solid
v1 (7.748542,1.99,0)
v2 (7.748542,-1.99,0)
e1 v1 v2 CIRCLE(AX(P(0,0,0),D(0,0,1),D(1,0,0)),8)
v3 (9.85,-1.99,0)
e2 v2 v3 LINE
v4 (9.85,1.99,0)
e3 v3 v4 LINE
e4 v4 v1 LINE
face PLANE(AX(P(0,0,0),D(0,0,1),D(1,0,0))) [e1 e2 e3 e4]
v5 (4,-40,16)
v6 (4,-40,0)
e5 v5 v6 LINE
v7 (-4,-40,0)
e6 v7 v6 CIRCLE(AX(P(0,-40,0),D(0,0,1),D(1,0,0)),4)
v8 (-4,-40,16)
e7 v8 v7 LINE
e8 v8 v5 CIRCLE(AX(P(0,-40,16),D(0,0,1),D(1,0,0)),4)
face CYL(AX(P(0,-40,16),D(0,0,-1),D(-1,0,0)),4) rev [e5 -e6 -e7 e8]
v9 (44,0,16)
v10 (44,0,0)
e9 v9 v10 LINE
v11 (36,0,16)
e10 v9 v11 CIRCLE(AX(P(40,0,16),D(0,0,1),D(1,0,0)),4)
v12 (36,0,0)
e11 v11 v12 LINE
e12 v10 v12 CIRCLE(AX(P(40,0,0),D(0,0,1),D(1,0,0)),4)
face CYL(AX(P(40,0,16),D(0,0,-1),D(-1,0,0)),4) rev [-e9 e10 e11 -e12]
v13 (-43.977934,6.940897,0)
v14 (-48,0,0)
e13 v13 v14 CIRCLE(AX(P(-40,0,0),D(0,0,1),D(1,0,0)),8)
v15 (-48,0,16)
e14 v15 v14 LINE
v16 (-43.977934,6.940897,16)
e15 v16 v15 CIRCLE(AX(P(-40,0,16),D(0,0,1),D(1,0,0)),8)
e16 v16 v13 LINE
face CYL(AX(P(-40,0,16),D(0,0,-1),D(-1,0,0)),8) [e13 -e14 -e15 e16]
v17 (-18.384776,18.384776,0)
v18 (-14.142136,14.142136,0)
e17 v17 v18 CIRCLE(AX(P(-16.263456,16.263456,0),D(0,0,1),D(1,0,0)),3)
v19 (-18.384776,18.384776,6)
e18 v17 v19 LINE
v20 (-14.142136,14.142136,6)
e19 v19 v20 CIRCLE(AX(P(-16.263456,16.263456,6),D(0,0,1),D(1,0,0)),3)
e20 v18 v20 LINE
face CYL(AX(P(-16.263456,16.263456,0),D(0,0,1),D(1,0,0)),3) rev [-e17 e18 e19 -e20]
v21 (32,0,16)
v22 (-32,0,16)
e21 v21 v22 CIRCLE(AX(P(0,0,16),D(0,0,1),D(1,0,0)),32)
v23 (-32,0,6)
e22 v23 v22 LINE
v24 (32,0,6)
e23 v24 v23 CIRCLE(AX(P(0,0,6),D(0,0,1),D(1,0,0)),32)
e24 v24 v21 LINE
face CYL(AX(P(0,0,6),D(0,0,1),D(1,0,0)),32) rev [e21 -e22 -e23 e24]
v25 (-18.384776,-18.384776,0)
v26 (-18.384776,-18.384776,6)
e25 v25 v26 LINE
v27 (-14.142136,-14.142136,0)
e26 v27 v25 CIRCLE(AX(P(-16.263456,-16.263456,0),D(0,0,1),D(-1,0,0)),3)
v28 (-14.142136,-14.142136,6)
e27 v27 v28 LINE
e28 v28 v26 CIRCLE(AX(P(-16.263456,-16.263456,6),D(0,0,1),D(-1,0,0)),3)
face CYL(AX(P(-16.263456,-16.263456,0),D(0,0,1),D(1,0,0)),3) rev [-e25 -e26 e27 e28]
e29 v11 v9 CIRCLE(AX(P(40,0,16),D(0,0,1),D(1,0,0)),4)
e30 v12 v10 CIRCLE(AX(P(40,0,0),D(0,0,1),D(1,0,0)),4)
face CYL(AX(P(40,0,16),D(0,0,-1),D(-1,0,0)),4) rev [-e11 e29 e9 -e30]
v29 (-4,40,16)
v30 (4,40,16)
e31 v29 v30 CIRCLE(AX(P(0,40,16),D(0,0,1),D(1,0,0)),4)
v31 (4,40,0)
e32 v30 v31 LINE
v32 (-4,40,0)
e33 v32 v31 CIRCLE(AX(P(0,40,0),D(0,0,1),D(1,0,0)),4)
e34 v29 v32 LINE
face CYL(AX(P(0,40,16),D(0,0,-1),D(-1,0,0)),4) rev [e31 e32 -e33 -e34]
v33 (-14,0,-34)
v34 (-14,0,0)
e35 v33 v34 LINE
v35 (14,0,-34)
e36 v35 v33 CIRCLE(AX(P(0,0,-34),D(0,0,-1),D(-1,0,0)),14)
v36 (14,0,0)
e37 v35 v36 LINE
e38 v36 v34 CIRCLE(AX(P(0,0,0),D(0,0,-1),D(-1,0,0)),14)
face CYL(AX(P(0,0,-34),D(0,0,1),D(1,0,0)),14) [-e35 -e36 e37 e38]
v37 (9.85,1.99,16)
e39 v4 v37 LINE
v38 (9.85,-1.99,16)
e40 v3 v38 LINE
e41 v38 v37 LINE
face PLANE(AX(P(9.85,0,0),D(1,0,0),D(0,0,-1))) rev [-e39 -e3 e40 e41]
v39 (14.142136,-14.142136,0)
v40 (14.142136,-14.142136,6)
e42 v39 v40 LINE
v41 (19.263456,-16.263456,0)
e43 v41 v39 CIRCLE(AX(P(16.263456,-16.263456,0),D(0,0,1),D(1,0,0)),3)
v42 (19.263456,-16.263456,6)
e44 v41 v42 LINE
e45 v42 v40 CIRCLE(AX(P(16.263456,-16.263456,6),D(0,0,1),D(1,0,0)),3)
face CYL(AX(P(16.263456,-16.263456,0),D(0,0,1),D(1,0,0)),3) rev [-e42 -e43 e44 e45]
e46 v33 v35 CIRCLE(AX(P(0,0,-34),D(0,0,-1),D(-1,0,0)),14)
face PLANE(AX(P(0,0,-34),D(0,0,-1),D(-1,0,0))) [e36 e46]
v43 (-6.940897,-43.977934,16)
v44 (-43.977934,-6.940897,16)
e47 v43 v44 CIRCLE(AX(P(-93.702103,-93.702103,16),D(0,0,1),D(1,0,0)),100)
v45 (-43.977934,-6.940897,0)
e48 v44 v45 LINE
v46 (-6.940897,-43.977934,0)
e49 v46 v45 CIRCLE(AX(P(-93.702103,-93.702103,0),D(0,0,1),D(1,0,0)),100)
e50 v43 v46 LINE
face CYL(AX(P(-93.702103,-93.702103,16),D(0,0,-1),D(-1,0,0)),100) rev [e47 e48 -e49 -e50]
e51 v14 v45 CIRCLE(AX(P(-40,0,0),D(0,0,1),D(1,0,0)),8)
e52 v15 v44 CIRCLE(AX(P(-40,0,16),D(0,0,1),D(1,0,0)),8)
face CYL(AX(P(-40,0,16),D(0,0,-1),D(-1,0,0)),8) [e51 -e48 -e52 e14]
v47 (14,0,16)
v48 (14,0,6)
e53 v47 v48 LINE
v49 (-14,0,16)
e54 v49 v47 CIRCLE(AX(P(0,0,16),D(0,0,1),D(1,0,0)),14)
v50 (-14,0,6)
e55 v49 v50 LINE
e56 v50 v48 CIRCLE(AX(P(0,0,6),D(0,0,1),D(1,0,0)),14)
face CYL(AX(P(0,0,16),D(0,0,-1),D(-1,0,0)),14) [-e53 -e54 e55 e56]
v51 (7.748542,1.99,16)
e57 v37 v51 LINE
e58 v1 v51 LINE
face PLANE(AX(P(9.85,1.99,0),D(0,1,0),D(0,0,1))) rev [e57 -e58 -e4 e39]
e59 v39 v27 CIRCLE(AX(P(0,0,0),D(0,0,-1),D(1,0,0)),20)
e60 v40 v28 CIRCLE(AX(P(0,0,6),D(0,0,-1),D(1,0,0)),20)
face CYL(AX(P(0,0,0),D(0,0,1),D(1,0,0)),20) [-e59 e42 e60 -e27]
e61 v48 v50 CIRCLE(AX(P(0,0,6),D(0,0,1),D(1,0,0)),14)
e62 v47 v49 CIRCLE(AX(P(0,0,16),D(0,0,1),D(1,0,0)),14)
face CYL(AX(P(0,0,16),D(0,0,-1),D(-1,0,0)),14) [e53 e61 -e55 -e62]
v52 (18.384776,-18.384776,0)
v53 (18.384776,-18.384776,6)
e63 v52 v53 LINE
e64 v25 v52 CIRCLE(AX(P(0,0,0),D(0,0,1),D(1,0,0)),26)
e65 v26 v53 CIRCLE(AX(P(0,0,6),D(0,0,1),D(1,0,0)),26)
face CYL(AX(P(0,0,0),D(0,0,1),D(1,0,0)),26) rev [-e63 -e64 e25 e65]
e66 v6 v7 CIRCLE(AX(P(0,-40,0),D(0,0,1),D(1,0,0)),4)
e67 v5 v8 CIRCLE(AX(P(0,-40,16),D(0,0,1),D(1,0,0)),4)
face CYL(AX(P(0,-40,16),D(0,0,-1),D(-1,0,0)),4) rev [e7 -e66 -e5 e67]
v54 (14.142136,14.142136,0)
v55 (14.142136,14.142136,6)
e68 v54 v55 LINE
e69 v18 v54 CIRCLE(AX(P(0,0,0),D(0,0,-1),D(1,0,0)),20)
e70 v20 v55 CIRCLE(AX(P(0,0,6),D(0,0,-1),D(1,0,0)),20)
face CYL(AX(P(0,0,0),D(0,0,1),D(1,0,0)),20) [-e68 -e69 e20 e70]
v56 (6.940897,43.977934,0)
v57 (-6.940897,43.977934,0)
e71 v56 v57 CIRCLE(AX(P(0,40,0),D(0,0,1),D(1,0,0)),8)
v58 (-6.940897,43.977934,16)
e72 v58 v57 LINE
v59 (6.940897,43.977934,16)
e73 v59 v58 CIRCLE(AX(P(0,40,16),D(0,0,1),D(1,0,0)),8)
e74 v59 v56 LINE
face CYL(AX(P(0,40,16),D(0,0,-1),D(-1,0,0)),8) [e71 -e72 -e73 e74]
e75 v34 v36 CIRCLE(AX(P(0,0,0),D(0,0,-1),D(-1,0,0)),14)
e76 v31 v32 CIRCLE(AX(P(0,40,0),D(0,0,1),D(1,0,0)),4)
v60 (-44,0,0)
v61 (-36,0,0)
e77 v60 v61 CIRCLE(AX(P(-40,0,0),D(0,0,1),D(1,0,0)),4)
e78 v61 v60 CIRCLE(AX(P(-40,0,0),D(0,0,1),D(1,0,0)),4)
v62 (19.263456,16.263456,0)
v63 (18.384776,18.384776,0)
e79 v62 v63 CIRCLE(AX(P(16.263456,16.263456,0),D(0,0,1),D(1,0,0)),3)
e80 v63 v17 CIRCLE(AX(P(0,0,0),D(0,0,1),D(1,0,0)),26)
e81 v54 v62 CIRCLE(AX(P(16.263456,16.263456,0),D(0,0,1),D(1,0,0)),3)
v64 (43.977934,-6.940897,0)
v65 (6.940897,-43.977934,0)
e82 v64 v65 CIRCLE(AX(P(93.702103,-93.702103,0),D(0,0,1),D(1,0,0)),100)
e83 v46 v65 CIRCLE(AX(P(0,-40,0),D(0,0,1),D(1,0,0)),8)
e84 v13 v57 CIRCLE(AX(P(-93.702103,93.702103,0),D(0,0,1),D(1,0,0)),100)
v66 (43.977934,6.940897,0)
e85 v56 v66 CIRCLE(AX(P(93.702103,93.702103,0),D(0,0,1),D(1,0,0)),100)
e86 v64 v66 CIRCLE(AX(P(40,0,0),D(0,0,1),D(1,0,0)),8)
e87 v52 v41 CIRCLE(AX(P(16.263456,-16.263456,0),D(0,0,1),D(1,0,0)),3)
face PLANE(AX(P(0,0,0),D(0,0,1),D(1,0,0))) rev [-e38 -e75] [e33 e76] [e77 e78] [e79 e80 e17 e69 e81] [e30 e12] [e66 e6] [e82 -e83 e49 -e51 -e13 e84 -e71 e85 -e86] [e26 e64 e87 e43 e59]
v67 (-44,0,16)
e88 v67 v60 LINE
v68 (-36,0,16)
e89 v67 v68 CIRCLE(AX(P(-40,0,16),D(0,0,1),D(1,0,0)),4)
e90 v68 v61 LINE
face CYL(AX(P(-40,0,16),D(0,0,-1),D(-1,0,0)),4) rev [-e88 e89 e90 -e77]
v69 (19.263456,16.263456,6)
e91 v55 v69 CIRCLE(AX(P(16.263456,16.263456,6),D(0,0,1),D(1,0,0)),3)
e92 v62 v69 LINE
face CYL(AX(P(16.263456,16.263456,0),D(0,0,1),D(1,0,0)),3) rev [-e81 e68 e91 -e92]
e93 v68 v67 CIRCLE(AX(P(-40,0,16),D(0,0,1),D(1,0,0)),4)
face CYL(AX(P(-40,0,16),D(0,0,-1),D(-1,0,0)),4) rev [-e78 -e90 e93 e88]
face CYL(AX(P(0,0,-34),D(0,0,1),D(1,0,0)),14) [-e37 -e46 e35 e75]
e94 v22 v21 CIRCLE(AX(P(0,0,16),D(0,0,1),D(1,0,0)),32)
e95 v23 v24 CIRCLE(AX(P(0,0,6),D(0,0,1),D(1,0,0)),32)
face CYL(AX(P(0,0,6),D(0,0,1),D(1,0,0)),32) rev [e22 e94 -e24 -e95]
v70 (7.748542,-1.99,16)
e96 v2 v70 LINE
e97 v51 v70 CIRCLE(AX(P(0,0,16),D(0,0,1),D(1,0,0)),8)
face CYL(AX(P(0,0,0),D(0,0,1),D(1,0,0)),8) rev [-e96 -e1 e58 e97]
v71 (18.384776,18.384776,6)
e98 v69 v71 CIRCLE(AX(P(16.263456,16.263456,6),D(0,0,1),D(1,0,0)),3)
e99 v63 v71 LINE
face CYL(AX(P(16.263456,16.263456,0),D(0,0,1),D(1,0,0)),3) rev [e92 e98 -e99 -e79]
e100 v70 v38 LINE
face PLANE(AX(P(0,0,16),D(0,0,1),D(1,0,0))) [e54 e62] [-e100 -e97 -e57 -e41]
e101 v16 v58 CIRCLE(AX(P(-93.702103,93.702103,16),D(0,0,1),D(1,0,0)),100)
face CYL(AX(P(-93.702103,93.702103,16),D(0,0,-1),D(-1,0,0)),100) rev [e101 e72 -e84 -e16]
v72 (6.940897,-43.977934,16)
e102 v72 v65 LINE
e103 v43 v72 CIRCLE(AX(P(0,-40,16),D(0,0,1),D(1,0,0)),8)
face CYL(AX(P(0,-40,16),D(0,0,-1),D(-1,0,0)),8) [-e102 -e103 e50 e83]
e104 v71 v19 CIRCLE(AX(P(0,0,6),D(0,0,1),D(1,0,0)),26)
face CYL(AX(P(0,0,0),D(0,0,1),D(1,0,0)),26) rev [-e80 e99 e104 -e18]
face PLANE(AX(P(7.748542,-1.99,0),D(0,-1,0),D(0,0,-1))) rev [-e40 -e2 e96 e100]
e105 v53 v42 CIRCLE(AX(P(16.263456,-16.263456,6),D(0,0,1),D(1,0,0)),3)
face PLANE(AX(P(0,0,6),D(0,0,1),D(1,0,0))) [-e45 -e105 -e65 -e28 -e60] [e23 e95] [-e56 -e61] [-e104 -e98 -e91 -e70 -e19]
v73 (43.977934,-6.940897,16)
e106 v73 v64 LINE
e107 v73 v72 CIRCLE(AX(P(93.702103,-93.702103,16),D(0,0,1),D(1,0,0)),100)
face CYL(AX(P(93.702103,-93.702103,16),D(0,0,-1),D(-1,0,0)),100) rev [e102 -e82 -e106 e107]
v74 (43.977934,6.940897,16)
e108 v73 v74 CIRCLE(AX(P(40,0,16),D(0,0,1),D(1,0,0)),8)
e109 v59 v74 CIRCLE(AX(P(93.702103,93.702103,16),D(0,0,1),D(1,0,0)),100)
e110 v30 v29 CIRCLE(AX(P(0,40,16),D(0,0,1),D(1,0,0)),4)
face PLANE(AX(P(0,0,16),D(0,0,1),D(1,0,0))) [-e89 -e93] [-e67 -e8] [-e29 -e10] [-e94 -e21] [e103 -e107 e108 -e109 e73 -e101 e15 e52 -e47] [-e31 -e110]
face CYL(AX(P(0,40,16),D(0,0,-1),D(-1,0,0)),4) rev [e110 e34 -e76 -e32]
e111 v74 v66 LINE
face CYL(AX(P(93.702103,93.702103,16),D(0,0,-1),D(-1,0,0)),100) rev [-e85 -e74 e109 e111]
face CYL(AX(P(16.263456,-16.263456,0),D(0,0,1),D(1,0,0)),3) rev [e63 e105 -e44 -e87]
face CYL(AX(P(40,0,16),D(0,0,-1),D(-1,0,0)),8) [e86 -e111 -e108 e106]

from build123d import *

# Parameters (mm, degrees)
FLANGE_PLATE_SKETCH_R    = 4
FLANGE_PLATE_SKETCH_R_2  = 32
FLANGE_PLATE_4_LUG_DEPTH = 16
FRONT_RECESS_32_SKETCH_R = 32
FRONT_RECESS_32_DEPTH    = 10
ARC_SLOTS_DEPTH          = 6
FRONT_HUB_14_SKETCH_R    = 14
FRONT_HUB_14_DEPTH       = 10
REAR_START               = 34
REAR_HUB_14_SKETCH_R     = 14
REAR_HUB_14_DEPTH        = 34
KEYED_BORE_8_DEPTH       = 16


with BuildPart() as part:
    # Flange Plate Sketch → Flange Plate 4-Lug (new body)
    # profile 1 of 2: a face of its own
    with BuildSketch(Plane.XY):
        with BuildLine():
            ThreePointArc((-6.940896525, -43.977933562), (-22.991424972, -22.991424972), (-43.977933562, -6.940896525))
            ThreePointArc((-43.977933562, -6.940896525), (-48, 0), (-43.977933562, 6.940896525))
            ThreePointArc((-43.977933562, 6.940896525), (-22.991424972, 22.991424972), (-6.940896525, 43.977933562))
            ThreePointArc((-6.940896525, 43.977933562), (0, 48), (6.940896525, 43.977933562))
            ThreePointArc((6.940896525, 43.977933562), (22.991424972, 22.991424972), (43.977933562, 6.940896525))
            ThreePointArc((43.977933562, 6.940896525), (48, 0), (43.977933562, -6.940896525))
            ThreePointArc((43.977933562, -6.940896525), (22.991424972, -22.991424972), (6.940896525, -43.977933562))
            ThreePointArc((6.940896525, -43.977933562), (0, -48), (-6.940896525, -43.977933562))
        make_face()
        with Locations((0, -40)):
            Circle(FLANGE_PLATE_SKETCH_R, mode=Mode.SUBTRACT)
        with Locations((-40, 0)):
            Circle(FLANGE_PLATE_SKETCH_R, mode=Mode.SUBTRACT)
        with Locations((40, 0)):
            Circle(FLANGE_PLATE_SKETCH_R, mode=Mode.SUBTRACT)
        with Locations((0, 40)):
            Circle(FLANGE_PLATE_SKETCH_R, mode=Mode.SUBTRACT)
        Circle(FLANGE_PLATE_SKETCH_R_2, mode=Mode.SUBTRACT)
    # profile 2 of 2: a face of its own
    with BuildSketch(Plane.XY):
        Circle(FLANGE_PLATE_SKETCH_R_2)
    extrude(amount=FLANGE_PLATE_4_LUG_DEPTH)

    # Front Recess Ø32 Sketch → Front Recess Ø32 (cut)
    with BuildSketch(Plane.XY.offset(16)):
        Circle(FRONT_RECESS_32_SKETCH_R)
    extrude(amount=-FRONT_RECESS_32_DEPTH, mode=Mode.SUBTRACT)

    # Arc Slots Sketch → Arc Slots (cut)
    with BuildSketch(Plane.XY.offset(6)):
        with BuildLine():
            ThreePointArc((-18.384776311, -18.384776311), (0, -26), (18.384776311, -18.384776311))
            ThreePointArc((18.384776311, -18.384776311), (18.384776311, -14.142135624), (14.142135624, -14.142135624))
            ThreePointArc((14.142135624, -14.142135624), (0, -20), (-14.142135624, -14.142135624))
            ThreePointArc((-14.142135624, -14.142135624), (-18.384776311, -14.142135624), (-18.384776311, -18.384776311))
        make_face()
        with BuildLine():
            ThreePointArc((14.142135624, 14.142135624), (0, 20), (-14.142135624, 14.142135624))
            ThreePointArc((-14.142135624, 14.142135624), (-18.384776311, 14.142135624), (-18.384776311, 18.384776311))
            ThreePointArc((-18.384776311, 18.384776311), (0, 26), (18.384776311, 18.384776311))
            ThreePointArc((18.384776311, 18.384776311), (18.384776311, 14.142135624), (14.142135624, 14.142135624))
        make_face()
    extrude(amount=-ARC_SLOTS_DEPTH, mode=Mode.SUBTRACT)

    # Front Hub Ø14 Sketch → Front Hub Ø14 (add)
    with BuildSketch(Plane.XY.offset(6)):
        Circle(FRONT_HUB_14_SKETCH_R)
    extrude(amount=FRONT_HUB_14_DEPTH)

    # Rear Hub Ø14 Sketch → Rear Hub Ø14 (add)
    with BuildSketch(Plane(origin=(0, 0, 0), x_dir=(-1, 0, 0), z_dir=(0, 0, -1)).offset(REAR_START)):
        with Locations(Location((0, 0, 0), (0, 0, 180))):
            Circle(REAR_HUB_14_SKETCH_R)
    extrude(amount=-REAR_HUB_14_DEPTH)

    # Keyed Bore Ø8 Sketch → Keyed Bore Ø8 (cut)
    with BuildSketch(Plane.XY.offset(16)):
        with BuildLine():
            Line((9.85, 0), (9.85, 1.99))
            Line((9.85, 1.99), (7.748541798, 1.99))
            ThreePointArc((7.748541798, 1.99), (-8, 0), (7.748541798, -1.99))
            Line((7.748541798, -1.99), (9.85, -1.99))
            Line((9.85, -1.99), (9.85, 0))
        make_face()
    extrude(amount=-KEYED_BORE_8_DEPTH, mode=Mode.SUBTRACT)


solid = part.part
